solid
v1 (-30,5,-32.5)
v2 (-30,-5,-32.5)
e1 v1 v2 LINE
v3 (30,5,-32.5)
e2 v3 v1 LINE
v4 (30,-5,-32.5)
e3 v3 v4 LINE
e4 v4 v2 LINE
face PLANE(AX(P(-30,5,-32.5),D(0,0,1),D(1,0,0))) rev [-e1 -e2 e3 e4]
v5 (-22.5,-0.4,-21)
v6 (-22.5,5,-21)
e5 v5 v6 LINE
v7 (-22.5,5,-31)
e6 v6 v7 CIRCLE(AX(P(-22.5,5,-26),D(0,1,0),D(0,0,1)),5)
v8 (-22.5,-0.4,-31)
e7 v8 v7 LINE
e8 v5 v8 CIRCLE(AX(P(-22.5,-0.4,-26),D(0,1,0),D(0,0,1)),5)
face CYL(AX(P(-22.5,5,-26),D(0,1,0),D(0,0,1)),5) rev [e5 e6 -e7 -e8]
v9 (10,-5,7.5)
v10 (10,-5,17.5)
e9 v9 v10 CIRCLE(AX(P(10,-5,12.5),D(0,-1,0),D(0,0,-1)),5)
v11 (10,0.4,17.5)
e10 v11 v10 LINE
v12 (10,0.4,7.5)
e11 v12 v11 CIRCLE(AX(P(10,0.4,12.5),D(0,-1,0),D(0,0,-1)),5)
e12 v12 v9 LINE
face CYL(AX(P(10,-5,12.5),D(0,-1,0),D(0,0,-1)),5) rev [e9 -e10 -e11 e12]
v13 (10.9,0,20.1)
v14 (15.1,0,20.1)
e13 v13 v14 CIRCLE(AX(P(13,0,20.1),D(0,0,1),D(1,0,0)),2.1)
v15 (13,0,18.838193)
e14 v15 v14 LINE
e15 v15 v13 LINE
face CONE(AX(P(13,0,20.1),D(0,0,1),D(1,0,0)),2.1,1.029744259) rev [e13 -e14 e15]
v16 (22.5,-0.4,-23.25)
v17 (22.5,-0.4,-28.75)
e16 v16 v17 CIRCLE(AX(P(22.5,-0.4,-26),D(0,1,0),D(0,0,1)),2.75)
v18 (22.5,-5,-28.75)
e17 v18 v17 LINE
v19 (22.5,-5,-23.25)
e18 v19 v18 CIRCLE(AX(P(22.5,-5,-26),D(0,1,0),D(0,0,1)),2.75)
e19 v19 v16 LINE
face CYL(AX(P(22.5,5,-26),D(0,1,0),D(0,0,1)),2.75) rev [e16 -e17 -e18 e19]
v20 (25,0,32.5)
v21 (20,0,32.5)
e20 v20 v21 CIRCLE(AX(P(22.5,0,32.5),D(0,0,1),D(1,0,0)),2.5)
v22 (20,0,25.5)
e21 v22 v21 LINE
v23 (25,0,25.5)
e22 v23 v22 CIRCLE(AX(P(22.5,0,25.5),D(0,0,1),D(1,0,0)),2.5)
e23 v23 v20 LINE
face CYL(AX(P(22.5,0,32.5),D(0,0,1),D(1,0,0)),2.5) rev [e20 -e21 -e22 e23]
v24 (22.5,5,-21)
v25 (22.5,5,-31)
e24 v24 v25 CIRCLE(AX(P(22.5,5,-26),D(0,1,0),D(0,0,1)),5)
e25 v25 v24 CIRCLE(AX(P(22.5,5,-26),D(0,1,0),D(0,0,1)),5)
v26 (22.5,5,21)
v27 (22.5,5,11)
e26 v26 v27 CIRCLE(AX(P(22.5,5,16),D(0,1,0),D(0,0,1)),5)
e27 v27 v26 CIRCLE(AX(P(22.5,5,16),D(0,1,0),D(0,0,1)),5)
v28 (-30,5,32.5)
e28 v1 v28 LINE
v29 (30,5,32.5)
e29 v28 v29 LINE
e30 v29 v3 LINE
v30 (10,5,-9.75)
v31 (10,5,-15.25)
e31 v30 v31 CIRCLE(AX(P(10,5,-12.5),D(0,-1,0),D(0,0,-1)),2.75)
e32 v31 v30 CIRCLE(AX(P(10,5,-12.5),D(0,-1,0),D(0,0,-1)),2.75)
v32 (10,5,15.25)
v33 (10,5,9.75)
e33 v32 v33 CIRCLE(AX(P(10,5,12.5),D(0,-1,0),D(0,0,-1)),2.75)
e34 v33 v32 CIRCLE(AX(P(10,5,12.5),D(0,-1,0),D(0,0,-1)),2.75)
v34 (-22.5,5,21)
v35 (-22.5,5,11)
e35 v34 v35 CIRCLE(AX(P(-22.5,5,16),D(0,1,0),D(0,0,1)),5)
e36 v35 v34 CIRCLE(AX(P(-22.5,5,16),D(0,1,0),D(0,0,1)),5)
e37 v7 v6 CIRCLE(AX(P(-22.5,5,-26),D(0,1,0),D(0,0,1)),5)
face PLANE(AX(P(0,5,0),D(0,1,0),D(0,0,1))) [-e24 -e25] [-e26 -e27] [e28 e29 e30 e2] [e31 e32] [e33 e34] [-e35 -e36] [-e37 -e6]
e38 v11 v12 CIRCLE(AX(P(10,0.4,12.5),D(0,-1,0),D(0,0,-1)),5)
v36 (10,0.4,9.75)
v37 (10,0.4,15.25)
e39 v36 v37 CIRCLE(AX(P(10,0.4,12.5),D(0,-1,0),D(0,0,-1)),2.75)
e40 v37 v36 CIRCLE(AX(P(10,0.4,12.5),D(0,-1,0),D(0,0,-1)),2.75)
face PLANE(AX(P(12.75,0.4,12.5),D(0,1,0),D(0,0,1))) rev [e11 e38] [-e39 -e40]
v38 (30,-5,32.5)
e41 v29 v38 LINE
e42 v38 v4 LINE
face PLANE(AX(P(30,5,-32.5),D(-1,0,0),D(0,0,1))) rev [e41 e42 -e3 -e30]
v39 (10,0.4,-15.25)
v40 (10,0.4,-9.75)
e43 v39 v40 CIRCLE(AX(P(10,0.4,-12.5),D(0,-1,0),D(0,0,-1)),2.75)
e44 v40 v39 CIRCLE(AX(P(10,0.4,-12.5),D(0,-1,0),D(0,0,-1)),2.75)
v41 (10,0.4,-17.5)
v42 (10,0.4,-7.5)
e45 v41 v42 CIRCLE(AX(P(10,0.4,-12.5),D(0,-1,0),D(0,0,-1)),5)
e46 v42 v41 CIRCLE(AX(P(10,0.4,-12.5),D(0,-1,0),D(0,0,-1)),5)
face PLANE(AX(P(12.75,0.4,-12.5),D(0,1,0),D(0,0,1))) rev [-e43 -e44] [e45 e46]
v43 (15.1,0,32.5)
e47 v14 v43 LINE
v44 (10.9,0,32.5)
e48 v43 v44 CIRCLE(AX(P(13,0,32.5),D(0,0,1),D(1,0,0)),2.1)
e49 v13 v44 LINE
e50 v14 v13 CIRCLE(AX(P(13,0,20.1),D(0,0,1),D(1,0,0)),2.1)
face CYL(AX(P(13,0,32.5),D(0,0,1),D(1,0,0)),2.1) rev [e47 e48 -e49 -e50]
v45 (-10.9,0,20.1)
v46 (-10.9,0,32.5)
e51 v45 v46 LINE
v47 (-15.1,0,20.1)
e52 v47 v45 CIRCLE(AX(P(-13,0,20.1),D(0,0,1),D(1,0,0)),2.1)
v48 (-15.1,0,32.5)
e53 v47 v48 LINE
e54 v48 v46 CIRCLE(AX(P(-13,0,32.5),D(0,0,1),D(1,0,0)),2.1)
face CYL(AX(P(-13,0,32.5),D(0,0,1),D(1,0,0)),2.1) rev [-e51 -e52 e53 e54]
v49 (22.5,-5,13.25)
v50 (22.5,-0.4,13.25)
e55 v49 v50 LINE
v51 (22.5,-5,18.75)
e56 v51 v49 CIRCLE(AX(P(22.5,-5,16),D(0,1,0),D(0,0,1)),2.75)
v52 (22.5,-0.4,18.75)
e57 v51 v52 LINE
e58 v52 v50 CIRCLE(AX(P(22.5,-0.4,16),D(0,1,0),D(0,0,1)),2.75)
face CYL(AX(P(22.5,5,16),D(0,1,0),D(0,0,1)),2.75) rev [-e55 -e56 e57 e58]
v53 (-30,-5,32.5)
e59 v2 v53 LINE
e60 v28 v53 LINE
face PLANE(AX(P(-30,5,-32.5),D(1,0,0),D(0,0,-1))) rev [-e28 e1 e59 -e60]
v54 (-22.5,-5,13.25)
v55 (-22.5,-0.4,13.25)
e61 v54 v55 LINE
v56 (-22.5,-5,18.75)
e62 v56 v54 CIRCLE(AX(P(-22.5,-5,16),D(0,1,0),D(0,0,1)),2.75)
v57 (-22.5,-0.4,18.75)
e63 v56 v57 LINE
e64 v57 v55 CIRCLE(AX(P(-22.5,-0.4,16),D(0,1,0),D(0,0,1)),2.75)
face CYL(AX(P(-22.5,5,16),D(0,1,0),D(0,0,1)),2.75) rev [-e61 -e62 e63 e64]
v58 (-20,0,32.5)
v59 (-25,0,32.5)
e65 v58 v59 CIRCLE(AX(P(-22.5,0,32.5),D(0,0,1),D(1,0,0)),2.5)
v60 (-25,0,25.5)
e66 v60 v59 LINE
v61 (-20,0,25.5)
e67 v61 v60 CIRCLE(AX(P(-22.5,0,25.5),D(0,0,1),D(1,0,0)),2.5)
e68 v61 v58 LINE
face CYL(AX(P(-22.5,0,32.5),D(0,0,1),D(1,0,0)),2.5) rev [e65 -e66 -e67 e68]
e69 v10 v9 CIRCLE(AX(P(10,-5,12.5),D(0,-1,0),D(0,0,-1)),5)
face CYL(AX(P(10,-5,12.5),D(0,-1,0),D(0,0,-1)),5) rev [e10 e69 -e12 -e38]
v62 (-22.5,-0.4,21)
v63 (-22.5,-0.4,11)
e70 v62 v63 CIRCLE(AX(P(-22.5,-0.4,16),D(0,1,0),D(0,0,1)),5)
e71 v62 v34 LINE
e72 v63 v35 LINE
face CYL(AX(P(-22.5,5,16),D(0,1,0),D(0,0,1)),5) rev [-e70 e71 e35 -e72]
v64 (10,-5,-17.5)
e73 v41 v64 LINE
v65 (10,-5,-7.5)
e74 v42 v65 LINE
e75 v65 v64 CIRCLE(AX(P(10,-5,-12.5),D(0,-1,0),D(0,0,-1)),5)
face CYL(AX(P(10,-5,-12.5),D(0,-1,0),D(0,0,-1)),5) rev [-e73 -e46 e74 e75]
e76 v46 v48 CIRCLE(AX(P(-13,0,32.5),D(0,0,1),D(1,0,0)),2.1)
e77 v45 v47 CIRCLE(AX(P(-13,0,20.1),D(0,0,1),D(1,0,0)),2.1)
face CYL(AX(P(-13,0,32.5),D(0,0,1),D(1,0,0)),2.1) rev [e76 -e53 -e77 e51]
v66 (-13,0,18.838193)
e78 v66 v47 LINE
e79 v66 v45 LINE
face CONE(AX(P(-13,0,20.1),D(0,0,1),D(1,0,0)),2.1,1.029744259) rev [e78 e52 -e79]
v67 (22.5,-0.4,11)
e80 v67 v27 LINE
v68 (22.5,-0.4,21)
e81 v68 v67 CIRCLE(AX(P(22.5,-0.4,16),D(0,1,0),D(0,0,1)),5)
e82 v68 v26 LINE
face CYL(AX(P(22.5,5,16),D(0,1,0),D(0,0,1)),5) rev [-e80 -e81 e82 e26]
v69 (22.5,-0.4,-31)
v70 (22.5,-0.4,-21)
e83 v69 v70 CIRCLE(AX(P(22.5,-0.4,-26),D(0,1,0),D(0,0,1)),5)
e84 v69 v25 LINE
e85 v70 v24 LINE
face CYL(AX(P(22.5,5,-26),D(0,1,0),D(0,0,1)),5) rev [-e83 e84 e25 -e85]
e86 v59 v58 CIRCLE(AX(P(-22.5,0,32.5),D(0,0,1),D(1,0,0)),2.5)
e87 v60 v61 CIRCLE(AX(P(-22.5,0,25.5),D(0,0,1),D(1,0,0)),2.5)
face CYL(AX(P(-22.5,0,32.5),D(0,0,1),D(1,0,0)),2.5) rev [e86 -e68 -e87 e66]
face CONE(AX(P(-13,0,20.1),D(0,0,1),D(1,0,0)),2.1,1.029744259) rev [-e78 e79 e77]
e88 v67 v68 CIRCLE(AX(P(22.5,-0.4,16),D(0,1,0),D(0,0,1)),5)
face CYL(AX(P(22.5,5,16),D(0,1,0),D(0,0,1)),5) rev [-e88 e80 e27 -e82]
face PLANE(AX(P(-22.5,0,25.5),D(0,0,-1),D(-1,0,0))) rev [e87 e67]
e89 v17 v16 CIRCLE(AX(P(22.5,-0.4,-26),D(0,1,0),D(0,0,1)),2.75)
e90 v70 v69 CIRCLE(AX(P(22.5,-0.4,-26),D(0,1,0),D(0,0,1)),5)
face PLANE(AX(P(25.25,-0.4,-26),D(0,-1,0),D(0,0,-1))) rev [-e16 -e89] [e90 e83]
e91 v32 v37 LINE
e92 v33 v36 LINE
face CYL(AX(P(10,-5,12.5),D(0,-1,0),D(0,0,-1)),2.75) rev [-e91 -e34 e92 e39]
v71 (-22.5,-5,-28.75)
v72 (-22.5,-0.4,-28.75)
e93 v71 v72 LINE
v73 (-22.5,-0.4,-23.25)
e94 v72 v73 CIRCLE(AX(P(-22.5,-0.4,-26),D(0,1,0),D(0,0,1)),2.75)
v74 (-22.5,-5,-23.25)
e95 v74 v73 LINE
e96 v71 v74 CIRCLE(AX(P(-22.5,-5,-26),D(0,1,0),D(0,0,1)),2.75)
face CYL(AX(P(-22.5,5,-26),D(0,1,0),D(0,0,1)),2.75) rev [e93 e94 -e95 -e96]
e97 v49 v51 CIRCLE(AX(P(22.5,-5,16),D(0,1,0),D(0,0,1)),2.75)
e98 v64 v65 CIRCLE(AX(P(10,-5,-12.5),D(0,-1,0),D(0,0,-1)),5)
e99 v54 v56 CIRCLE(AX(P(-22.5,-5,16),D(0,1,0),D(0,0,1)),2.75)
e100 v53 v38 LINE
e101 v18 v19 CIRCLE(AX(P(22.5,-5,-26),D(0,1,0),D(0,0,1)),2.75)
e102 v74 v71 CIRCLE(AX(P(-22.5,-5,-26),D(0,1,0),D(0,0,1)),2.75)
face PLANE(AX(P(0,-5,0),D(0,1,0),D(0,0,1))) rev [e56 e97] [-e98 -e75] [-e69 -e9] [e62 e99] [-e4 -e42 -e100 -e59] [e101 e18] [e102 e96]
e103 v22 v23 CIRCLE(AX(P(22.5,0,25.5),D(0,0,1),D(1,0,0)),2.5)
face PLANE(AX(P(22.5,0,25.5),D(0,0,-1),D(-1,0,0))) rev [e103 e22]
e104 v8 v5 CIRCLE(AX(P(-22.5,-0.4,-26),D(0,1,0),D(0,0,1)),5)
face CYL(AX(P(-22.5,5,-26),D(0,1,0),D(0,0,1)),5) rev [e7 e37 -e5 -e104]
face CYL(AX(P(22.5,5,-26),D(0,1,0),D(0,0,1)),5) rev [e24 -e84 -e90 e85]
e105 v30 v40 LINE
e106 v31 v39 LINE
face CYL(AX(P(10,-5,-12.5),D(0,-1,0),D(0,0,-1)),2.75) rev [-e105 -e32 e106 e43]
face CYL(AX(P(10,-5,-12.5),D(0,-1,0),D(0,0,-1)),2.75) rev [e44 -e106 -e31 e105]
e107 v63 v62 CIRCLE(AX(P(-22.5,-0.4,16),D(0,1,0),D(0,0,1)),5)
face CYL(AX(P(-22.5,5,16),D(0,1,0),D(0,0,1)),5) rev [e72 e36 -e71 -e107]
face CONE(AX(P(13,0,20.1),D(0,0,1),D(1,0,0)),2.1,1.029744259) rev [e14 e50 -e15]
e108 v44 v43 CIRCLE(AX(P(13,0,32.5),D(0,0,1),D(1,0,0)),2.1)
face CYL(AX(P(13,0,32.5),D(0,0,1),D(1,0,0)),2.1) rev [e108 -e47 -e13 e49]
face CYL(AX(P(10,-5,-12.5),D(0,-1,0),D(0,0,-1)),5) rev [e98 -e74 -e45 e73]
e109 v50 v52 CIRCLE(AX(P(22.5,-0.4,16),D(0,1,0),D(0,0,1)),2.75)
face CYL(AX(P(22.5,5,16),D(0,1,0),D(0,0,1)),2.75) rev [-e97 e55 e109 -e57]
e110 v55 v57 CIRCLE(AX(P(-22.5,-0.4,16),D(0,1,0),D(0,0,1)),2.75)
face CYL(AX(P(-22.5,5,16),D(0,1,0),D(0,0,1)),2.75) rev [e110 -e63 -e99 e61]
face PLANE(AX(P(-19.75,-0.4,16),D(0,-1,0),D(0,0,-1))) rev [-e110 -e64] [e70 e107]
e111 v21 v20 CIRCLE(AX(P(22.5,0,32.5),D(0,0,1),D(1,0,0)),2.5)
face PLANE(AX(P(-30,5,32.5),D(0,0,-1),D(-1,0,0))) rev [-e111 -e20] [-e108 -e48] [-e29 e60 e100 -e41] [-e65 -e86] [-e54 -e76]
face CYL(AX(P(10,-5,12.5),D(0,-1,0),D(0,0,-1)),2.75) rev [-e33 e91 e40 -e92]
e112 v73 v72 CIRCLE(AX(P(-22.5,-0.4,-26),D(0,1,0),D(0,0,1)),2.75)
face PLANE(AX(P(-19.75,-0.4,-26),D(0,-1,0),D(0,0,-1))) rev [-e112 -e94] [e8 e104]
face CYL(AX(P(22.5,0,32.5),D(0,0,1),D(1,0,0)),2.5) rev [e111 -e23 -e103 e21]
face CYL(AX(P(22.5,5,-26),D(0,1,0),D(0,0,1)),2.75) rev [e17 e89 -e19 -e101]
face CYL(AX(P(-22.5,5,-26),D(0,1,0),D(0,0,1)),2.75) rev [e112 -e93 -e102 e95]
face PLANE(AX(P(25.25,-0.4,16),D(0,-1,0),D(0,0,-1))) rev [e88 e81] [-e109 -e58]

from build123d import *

# Parameters (mm, degrees)
SKETCH_1_W                   = 60
SKETCH_1_H                   = 65
EXTRUDE_1_DEPTH              = 5
HOLE_WIZARD_M5_1_D           = 5.5
HOLE_WIZARD_M5_1_CBORE_D     = 10
HOLE_WIZARD_M5_1_CBORE_DEPTH = 5.4
F_5_0MM_1_D                  = 5
F_5_0MM_1_DEPTH              = 7
HOLE_WIZARD_M5_1_2_D         = 4.2
HOLE_WIZARD_M5_1_2_DEPTH     = 12.4
HOLE_WIZARD_M5_1_2_TIP       = 1.2618073
HOLE_WIZARD_M5_2_D           = 5.5
HOLE_WIZARD_M5_2_CBORE_D     = 10
HOLE_WIZARD_M5_2_CBORE_DEPTH = 5.4


with BuildPart() as part:
    # 草图1 → 凸台-拉伸1 (new, symmetric)
    with BuildSketch(Plane(origin=(0, 0, 0), x_dir=(1, 0, 0), z_dir=(0, 1, 0))):
        Rectangle(SKETCH_1_W, SKETCH_1_H)
    extrude(amount=EXTRUDE_1_DEPTH, both=True)

    # Hole Wizard M5 _1 (through all)
    with Locations(Plane(origin=(0, 5, 0), x_dir=(1, 0, 0), z_dir=(0, 1, 0))):
        with Locations((-22.5, 26), (-22.5, -16), (22.5, -16), (22.5, 26)):
            CounterBoreHole(HOLE_WIZARD_M5_1_D / 2, HOLE_WIZARD_M5_1_CBORE_D / 2, HOLE_WIZARD_M5_1_CBORE_DEPTH)

    # Ø5.0mm 暗销孔1
    with Locations(Plane.XY.offset(32.5)):
        with Locations((-22.5, 0), (22.5, 0)):
            Hole(F_5_0MM_1_D / 2, depth=F_5_0MM_1_DEPTH)

    # Hole Wizard M5 _1 2
    with Locations(Plane.XY.offset(32.5)):
        with Locations((-13, 0), (13, 0)):
            Hole(HOLE_WIZARD_M5_1_2_D / 2, depth=HOLE_WIZARD_M5_1_2_DEPTH)
            with Locations((0, 0, -(HOLE_WIZARD_M5_1_2_DEPTH + HOLE_WIZARD_M5_1_2_TIP / 2))):  # 118° drill point
                Cone(0, HOLE_WIZARD_M5_1_2_D / 2, HOLE_WIZARD_M5_1_2_TIP, mode=Mode.SUBTRACT)

    # M5 六角凹头螺钉的柱形沉头孔2 (through all)
    with Locations(Plane(origin=(0, -5, 0), x_dir=(-1, 0, 0), z_dir=(0, -1, 0))):
        with Locations((-10, -12.5), (-10, 12.5)):
            CounterBoreHole(HOLE_WIZARD_M5_2_D / 2, HOLE_WIZARD_M5_2_CBORE_D / 2, HOLE_WIZARD_M5_2_CBORE_DEPTH)


solid = part.part
